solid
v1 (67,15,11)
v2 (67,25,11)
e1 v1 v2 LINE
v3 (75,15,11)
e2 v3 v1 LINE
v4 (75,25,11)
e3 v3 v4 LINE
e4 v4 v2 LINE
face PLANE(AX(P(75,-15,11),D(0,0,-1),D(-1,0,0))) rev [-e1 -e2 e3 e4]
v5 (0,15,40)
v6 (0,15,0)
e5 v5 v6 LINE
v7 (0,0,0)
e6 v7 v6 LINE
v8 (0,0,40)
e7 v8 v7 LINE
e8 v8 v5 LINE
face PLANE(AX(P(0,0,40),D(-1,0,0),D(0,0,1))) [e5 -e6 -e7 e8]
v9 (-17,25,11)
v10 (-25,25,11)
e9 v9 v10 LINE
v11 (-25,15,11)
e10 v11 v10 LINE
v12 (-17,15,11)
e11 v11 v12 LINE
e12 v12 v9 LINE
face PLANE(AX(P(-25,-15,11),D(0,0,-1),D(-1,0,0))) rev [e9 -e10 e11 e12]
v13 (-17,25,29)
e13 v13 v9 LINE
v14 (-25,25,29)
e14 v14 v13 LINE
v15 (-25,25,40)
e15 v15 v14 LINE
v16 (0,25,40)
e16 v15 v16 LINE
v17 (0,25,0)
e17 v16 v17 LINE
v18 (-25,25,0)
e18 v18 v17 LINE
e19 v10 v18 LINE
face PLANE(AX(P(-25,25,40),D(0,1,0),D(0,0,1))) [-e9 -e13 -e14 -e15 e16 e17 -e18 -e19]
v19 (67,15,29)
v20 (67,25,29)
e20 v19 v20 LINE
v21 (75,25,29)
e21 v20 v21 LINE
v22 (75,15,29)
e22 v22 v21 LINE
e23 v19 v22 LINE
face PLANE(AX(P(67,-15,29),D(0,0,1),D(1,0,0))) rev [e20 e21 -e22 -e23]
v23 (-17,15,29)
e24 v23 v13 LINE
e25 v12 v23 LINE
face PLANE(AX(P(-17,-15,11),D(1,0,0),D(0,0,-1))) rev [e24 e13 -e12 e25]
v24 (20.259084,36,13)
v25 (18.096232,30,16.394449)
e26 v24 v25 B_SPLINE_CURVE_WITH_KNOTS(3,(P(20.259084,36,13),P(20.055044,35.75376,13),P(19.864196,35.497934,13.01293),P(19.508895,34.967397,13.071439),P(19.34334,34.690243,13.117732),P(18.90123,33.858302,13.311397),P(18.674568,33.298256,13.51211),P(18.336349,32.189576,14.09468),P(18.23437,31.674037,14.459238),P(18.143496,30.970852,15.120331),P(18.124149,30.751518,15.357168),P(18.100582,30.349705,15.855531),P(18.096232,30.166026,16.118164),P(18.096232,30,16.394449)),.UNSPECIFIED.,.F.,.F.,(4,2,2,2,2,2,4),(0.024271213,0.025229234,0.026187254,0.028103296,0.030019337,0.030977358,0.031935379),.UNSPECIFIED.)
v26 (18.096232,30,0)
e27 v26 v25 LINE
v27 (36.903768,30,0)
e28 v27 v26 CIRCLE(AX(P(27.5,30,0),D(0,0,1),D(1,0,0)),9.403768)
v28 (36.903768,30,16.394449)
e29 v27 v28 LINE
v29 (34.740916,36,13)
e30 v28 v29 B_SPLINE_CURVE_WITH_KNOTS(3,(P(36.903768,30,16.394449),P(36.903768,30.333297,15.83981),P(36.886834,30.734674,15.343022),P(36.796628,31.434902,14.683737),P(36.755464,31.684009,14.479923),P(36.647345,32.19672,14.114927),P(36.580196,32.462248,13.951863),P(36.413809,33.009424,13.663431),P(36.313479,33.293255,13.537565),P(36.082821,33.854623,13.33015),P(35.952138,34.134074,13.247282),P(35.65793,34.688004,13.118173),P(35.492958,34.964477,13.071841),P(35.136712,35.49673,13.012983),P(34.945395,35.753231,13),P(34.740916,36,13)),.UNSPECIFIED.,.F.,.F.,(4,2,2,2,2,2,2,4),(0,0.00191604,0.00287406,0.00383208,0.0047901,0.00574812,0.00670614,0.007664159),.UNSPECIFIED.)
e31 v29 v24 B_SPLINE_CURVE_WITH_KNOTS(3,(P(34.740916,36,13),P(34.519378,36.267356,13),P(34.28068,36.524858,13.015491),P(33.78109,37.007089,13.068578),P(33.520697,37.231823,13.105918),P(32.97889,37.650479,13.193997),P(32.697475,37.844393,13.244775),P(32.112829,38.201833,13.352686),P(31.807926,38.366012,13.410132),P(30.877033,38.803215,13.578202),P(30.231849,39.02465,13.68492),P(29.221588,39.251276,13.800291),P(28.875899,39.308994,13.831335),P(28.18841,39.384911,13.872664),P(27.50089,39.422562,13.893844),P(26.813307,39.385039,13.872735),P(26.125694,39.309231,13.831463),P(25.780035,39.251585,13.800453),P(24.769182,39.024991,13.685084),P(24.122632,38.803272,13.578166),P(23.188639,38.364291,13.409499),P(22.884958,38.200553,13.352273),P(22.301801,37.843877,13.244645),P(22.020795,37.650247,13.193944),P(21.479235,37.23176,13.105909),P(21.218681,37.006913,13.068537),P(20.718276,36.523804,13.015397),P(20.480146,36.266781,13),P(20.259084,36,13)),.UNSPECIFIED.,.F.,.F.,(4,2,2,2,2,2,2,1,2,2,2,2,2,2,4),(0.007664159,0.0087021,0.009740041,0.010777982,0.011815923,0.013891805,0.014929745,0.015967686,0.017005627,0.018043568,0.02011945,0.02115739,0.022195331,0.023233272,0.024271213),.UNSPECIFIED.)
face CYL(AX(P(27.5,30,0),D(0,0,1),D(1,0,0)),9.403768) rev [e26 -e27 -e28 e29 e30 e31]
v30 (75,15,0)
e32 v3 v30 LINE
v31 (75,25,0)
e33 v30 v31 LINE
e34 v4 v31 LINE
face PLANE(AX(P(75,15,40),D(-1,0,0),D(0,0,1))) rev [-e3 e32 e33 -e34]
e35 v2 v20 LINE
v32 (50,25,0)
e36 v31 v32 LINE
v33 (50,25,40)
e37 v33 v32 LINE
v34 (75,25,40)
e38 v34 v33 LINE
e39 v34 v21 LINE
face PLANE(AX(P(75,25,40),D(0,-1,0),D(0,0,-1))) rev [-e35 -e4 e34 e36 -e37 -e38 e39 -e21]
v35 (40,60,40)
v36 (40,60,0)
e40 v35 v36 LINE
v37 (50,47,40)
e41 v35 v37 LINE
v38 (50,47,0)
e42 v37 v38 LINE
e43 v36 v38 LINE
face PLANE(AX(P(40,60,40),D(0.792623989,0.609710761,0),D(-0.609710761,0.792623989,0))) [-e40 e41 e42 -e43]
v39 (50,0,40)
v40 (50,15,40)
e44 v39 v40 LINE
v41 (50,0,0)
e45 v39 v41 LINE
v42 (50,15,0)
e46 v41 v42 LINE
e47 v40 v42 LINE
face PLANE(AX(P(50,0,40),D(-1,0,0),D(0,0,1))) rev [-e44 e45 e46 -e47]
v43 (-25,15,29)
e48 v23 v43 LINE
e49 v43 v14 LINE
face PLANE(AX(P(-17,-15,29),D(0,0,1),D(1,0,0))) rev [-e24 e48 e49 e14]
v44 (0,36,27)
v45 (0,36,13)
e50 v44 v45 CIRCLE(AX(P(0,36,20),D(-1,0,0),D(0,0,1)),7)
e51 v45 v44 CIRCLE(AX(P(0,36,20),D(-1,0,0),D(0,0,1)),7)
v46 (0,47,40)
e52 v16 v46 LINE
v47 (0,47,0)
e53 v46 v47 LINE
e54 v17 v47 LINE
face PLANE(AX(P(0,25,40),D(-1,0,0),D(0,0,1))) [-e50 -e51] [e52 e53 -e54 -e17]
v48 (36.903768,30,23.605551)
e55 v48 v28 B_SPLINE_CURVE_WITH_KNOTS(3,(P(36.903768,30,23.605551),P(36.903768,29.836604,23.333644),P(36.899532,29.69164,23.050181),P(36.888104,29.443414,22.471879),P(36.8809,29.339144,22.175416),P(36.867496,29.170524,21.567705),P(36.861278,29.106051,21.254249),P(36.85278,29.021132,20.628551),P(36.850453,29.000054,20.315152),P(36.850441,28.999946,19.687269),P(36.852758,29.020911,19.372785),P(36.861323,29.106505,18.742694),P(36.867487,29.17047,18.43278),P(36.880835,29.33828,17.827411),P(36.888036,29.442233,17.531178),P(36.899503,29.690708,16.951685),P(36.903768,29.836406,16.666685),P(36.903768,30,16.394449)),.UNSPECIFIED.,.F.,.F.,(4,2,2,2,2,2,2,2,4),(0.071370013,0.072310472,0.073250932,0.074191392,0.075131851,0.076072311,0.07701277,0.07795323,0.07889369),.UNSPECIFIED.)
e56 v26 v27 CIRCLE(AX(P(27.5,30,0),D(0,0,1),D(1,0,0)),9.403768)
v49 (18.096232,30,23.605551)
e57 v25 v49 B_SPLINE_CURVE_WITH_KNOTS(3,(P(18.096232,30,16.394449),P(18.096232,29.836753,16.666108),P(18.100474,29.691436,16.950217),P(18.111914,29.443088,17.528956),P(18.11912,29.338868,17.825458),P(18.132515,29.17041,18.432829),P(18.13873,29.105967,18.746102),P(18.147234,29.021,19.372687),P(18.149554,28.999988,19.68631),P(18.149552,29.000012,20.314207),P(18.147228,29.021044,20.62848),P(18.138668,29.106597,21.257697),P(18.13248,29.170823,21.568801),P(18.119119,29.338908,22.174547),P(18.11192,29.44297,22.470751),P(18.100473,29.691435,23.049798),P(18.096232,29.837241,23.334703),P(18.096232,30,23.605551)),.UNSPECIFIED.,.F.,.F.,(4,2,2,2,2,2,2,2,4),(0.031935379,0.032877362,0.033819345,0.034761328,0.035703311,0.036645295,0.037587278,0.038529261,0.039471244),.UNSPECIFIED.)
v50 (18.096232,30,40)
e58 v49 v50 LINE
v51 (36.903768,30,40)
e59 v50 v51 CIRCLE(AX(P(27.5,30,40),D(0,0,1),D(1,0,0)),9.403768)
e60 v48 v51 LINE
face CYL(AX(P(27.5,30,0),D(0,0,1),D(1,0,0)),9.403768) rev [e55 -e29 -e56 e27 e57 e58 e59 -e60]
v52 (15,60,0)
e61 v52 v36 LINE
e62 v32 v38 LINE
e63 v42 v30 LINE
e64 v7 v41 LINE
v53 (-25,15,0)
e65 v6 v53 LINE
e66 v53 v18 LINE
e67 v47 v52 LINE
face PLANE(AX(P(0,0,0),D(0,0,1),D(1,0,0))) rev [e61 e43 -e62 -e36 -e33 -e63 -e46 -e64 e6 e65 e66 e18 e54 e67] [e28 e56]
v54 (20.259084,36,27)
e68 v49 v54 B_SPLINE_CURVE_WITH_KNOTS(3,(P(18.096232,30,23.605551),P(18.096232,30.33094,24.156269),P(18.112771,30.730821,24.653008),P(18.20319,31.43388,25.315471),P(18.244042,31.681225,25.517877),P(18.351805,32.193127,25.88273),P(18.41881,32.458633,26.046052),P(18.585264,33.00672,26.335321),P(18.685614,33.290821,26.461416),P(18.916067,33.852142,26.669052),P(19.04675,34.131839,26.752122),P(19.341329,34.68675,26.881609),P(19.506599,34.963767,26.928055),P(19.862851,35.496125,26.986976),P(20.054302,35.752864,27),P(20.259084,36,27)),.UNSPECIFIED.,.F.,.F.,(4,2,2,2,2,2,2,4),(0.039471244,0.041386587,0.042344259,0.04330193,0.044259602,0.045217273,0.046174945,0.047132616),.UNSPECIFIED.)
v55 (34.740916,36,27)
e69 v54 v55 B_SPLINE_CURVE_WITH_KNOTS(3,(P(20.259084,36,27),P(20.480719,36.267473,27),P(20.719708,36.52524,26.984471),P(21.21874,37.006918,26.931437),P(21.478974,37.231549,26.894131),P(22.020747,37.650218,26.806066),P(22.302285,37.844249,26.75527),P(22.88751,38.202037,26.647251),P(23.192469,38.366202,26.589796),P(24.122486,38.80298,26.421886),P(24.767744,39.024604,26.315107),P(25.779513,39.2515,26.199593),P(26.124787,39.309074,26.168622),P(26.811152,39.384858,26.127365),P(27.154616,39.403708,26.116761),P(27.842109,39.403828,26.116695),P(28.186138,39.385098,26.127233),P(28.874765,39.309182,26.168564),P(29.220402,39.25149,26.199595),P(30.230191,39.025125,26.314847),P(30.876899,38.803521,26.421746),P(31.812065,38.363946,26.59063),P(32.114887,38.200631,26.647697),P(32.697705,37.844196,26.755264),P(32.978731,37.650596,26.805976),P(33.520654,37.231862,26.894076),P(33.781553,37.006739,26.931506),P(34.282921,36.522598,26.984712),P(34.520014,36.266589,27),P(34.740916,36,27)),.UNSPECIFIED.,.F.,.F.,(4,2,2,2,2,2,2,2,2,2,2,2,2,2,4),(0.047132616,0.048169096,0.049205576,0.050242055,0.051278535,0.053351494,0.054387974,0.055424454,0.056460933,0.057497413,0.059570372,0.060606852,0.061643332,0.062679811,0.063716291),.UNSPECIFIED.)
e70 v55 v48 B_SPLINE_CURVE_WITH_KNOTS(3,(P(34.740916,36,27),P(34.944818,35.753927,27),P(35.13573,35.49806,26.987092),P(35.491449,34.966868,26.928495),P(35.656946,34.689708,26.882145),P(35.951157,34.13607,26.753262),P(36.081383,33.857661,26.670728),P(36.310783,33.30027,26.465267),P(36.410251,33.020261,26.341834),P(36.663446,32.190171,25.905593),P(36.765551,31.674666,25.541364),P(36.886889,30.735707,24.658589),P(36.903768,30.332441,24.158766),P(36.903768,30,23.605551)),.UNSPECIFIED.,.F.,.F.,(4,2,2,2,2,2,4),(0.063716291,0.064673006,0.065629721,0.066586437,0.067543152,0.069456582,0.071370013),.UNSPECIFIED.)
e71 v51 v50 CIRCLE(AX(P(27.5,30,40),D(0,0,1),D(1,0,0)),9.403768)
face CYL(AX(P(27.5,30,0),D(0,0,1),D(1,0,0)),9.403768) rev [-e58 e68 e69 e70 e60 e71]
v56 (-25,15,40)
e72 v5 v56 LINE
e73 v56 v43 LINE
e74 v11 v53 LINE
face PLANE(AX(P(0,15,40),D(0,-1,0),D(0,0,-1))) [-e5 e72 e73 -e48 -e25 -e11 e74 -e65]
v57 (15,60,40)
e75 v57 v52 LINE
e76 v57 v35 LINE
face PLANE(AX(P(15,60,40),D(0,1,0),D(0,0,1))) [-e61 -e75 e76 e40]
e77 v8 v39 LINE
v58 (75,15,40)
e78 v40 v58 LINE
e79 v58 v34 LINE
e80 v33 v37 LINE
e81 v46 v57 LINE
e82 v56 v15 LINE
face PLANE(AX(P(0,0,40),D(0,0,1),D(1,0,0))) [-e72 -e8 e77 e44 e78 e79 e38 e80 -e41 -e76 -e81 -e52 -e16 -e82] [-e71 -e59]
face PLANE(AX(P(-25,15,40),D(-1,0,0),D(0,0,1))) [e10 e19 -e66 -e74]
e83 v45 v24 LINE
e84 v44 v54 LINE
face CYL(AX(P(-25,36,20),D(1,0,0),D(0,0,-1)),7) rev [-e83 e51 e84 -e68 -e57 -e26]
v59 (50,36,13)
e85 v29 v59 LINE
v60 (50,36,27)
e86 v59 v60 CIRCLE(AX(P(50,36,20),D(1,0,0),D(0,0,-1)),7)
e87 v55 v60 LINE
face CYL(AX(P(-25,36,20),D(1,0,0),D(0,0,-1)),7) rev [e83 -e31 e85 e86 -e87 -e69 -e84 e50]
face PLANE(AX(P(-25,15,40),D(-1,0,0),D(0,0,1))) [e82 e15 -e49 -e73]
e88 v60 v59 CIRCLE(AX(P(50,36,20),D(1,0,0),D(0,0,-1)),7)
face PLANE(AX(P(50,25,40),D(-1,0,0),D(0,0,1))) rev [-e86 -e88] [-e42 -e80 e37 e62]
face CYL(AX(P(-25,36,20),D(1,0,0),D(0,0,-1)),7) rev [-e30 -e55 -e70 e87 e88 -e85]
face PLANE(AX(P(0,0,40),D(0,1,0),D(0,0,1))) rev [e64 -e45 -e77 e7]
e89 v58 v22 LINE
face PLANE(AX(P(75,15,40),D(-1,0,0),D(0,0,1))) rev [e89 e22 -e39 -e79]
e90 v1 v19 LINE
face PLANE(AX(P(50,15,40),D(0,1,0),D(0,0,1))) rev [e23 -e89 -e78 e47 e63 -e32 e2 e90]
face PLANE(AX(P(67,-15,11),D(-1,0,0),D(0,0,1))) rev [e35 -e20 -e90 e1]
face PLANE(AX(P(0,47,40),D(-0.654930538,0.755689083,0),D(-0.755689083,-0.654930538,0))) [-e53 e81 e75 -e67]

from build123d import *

# Parameters (mm, degrees)
BRACKET_BODY_DEPTH      = 40
FRONT_BORE_SKETCH_R     = 9.403768256
FRONT_BORE_DEPTH        = 105.043260233
FLANGE_NOTCH_SKETCH_W   = 8
FLANGE_NOTCH_SKETCH_H   = 18
FLANGE_NOTCH_CUTS_DEPTH = 40
FLANGE_SLOT_SKETCH_W    = 8
FLANGE_SLOT_SKETCH_H    = 18
FLANGE_SLOT_CUT_DEPTH   = 40
CROSS_HOLE_SKETCH_R     = 7
CROSS_HOLE_14_DEPTH     = 105.043260233


with BuildPart() as part:
    # Bracket Profile Sketch → Bracket Body (new body)
    with BuildSketch(Plane.XY):
        Polygon((0, 0), (50, 0), (50, 15), (75, 15), (75, 25), (50, 25), (50, 47), (40, 60), (15, 60), (0, 47), (0, 25), (-25, 25), (-25, 15), (0, 15), align=None)
    extrude(amount=BRACKET_BODY_DEPTH)

    # Front Bore Sketch → Front Bore (cut, through all)
    with BuildSketch(Plane.XY.offset(40)):
        with Locations((27.5, 30)):
            Circle(FRONT_BORE_SKETCH_R)
    extrude(amount=-FRONT_BORE_DEPTH, mode=Mode.SUBTRACT)

    # Flange Notch Sketch → Flange Notch Cuts (cut)
    with BuildSketch(Plane(origin=(0, 25, 0), x_dir=(1, 0, 0), z_dir=(0, 1, 0))):
        with Locations((71, -20)):
            Rectangle(FLANGE_NOTCH_SKETCH_W, FLANGE_NOTCH_SKETCH_H)
    extrude(amount=-FLANGE_NOTCH_CUTS_DEPTH, mode=Mode.SUBTRACT)

    # Flange Slot Sketch → Flange Slot Cut (cut)
    with BuildSketch(Plane(origin=(0, 25, 0), x_dir=(1, 0, 0), z_dir=(0, 1, 0))):
        with Locations((-21, -20)):
            Rectangle(FLANGE_SLOT_SKETCH_W, FLANGE_SLOT_SKETCH_H)
    extrude(amount=-FLANGE_SLOT_CUT_DEPTH, mode=Mode.SUBTRACT)

    # Cross Hole Sketch → Cross Hole Ø14 (cut, through all)
    with BuildSketch(Plane(origin=(50, 0, 0), x_dir=(0, 0, -1), z_dir=(1, 0, 0))):
        with Locations((-20, 36)):
            Circle(CROSS_HOLE_SKETCH_R)
    extrude(amount=-CROSS_HOLE_14_DEPTH, mode=Mode.SUBTRACT)


solid = part.part
